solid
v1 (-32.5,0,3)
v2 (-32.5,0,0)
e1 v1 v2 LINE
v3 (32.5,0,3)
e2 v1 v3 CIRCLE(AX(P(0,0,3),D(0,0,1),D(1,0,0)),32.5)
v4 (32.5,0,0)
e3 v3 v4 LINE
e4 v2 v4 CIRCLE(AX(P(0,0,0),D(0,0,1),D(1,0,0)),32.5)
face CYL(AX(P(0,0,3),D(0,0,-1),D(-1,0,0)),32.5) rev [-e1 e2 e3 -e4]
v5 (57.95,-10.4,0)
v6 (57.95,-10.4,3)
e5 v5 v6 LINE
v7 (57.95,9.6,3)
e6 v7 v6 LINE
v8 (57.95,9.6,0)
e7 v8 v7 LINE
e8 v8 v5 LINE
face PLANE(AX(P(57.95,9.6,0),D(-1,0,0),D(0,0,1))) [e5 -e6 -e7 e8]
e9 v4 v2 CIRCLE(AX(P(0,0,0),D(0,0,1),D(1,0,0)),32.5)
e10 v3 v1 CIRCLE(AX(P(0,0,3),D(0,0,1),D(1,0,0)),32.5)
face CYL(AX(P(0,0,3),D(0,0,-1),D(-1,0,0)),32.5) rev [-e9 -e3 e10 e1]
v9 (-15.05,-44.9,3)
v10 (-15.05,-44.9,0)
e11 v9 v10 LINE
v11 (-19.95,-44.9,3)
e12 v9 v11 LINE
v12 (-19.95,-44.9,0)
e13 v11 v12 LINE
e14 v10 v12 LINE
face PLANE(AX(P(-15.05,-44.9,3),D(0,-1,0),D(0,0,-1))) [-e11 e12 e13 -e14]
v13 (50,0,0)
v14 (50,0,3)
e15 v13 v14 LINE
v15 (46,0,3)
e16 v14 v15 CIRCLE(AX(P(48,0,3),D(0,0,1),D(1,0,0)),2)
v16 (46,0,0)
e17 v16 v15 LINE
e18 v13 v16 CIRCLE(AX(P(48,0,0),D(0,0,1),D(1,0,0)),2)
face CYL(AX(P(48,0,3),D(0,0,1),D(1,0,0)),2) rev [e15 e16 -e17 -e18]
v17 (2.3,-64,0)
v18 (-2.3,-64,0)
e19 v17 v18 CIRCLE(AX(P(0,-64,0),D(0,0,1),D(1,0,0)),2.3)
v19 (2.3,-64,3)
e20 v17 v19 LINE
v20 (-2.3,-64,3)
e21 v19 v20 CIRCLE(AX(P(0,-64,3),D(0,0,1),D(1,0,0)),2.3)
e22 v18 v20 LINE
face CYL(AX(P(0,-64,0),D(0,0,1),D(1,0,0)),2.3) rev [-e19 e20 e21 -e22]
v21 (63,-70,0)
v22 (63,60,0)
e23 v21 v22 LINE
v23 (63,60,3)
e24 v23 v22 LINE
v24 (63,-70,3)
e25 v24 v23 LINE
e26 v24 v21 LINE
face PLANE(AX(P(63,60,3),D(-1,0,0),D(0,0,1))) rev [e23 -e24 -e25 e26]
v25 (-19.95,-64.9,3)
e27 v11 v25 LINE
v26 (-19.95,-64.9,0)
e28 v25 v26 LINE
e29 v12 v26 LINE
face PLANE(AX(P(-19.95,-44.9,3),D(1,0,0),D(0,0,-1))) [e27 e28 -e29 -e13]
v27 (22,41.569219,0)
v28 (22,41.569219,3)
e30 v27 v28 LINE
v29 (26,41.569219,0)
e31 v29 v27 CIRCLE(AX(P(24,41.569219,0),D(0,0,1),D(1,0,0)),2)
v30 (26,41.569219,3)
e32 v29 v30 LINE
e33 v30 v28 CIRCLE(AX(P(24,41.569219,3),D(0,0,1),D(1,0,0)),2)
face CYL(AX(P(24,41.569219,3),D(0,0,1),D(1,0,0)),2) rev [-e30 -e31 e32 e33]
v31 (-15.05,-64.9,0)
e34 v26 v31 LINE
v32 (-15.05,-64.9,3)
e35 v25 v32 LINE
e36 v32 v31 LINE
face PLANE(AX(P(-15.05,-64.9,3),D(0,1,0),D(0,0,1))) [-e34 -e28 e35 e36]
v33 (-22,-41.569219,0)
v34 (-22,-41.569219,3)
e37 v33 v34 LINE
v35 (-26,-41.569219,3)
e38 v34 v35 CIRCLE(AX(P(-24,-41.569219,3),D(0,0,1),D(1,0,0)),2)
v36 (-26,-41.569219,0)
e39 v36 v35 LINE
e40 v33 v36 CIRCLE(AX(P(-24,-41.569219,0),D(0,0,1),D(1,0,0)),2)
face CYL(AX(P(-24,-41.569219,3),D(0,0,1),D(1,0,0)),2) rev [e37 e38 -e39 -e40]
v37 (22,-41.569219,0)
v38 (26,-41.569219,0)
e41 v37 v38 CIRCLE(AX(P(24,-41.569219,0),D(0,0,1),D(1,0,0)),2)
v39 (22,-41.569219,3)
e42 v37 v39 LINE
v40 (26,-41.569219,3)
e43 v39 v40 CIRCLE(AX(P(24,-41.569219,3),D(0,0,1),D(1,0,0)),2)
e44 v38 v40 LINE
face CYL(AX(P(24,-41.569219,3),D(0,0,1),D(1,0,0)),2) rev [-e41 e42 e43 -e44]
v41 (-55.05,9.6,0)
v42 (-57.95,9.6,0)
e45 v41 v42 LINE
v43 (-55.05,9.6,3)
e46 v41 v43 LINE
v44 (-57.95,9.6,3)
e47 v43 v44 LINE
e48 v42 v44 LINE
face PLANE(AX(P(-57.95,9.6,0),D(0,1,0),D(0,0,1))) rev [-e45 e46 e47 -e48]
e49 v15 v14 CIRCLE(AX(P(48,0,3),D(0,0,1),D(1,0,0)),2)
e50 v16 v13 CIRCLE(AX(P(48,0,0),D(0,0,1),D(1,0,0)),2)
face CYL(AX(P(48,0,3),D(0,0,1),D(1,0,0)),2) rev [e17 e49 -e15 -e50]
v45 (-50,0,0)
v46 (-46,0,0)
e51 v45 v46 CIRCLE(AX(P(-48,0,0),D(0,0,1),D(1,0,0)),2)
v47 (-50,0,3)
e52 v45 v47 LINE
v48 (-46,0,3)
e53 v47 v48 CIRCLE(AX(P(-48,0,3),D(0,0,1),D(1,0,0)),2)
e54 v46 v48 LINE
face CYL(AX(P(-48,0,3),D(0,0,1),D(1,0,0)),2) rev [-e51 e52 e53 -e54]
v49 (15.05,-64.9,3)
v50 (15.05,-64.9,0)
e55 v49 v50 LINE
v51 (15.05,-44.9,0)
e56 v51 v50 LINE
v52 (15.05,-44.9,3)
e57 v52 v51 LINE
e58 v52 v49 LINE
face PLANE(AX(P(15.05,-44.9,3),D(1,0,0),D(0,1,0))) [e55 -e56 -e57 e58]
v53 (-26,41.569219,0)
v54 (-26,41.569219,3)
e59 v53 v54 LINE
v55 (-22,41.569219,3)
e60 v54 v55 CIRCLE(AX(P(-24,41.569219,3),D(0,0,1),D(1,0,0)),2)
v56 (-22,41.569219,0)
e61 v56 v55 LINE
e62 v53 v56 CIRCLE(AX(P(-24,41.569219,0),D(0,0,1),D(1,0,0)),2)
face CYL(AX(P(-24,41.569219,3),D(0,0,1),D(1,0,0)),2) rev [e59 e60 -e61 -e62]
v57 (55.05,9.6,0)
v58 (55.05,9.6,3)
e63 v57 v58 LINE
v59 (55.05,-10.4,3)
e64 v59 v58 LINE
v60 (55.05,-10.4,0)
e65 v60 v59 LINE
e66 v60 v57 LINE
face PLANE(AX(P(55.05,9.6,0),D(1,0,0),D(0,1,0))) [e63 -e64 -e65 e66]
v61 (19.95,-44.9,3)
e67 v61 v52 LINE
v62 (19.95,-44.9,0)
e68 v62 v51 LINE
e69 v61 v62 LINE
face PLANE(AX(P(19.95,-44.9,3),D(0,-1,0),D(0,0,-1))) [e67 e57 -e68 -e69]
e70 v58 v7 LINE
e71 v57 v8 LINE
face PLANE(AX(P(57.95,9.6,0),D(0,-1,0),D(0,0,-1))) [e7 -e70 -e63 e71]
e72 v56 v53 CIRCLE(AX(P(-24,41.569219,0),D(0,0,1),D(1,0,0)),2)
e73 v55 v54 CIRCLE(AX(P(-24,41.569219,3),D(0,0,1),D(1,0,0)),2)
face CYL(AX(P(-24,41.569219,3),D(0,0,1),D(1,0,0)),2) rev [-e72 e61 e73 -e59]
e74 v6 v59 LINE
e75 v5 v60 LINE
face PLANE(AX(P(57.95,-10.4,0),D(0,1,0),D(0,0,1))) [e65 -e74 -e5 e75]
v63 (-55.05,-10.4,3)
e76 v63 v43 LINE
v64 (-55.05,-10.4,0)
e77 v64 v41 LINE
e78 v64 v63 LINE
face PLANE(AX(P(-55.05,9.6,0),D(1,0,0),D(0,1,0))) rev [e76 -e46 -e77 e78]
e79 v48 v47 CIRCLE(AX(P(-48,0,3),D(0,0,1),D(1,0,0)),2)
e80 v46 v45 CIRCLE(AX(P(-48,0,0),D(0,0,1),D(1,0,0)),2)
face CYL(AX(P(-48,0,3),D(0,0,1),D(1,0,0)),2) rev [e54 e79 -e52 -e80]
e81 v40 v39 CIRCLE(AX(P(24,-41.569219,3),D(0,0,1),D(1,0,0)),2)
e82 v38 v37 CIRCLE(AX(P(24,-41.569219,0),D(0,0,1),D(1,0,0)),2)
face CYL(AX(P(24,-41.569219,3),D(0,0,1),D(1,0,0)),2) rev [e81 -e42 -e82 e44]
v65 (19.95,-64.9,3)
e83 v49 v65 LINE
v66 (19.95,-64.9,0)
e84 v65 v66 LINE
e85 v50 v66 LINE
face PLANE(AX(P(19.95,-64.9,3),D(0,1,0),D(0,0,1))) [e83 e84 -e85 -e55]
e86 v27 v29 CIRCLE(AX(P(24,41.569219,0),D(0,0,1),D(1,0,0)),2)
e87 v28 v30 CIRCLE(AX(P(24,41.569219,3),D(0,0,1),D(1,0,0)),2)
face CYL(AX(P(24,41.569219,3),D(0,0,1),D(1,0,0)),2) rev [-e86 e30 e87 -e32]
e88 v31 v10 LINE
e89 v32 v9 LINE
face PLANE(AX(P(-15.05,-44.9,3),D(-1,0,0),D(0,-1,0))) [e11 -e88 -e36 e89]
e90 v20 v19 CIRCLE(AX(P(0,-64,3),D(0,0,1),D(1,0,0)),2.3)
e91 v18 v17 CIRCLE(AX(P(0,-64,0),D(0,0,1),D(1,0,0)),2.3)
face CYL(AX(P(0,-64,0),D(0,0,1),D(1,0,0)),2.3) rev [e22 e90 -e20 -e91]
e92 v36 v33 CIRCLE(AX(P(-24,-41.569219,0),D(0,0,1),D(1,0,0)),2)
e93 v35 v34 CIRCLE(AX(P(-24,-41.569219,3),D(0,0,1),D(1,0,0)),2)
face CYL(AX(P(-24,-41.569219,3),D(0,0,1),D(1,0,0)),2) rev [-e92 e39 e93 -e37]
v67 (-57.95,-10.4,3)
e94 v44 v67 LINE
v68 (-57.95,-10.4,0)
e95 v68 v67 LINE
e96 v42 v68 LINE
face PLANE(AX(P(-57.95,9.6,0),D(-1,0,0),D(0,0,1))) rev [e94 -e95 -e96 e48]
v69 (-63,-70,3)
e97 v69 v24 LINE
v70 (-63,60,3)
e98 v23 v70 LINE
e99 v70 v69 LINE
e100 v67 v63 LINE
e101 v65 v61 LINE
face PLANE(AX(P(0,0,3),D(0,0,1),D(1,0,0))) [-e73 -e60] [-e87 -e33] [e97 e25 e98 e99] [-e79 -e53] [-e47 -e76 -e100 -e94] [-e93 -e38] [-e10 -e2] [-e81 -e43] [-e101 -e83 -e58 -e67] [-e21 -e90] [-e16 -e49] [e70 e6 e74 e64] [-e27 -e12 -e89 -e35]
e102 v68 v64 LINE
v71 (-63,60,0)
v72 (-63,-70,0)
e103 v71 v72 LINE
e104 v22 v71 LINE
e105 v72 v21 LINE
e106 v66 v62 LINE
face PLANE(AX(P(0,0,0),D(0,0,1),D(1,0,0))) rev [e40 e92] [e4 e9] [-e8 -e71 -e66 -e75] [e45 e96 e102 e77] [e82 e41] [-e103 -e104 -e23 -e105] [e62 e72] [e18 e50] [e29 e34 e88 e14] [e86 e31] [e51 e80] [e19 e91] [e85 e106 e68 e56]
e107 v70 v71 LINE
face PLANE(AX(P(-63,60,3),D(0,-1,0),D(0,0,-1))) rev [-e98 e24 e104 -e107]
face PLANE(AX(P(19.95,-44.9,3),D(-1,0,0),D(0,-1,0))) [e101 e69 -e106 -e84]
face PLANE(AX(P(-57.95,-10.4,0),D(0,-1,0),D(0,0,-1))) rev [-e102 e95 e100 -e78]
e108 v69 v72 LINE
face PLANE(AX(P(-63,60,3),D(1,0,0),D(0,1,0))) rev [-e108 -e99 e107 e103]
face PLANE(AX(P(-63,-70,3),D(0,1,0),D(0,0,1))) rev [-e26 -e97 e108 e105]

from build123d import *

# Parameters (mm, degrees)
SKETCH1_W                    = 126
SKETCH1_H                    = 130
SKETCH1_R                    = 32.5
SKETCH1_W_2                  = 4.9
SKETCH1_H_2                  = 20
BOSS_EXTRUDE1_DEPTH          = 3
SKETCH2_W                    = 2.9
SKETCH2_H                    = 20
CUT_EXTRUDE1_DEPTH           = 3
F_4_0_4_DIAMETER_HOLE1_D     = 4
F_4_0_4_DIAMETER_HOLE1_DEPTH = 10
F_4_0_4_DIAMETER_HOLE1_TIP   = 1.201721238
SKETCH6_R                    = 2.3
CUT_EXTRUDE2_DEPTH           = 3


with BuildPart() as part:
    # Sketch1 → Boss-Extrude1 (new body)
    with BuildSketch(Plane.XY):
        with Locations((0, -5)):
            Rectangle(SKETCH1_W, SKETCH1_H)
        Circle(SKETCH1_R, mode=Mode.SUBTRACT)
        with Locations((-17.5, -54.9)):
            Rectangle(SKETCH1_W_2, SKETCH1_H_2, mode=Mode.SUBTRACT)
        with Locations((17.5, -54.9)):
            Rectangle(SKETCH1_W_2, SKETCH1_H_2, mode=Mode.SUBTRACT)
    extrude(amount=BOSS_EXTRUDE1_DEPTH)

    # Sketch2 → Cut-Extrude1 (cut)
    with BuildSketch(Plane.XY.offset(3)):
        with Locations((-56.5, -0.4)):
            Rectangle(SKETCH2_W, SKETCH2_H)
    cut_extrude1 = extrude(amount=-CUT_EXTRUDE1_DEPTH, mode=Mode.SUBTRACT)

    # Mirror1: Cut-Extrude1 across plane
    add(cut_extrude1.mirror(Plane(origin=(0, 0, 0), x_dir=(0, 0, 1), z_dir=(1, 0, 0))), mode=Mode.SUBTRACT)

    # Ø4.0 (4) Diameter Hole1
    with Locations(Plane.XY.offset(3)):
        with Locations((-24, 41.569219382), (48, 0), (24, 41.569219382), (24, -41.569219382), (-24, -41.569219382), (-48, 0)):
            Hole(F_4_0_4_DIAMETER_HOLE1_D / 2, depth=F_4_0_4_DIAMETER_HOLE1_DEPTH)
            with Locations((0, 0, -(F_4_0_4_DIAMETER_HOLE1_DEPTH + F_4_0_4_DIAMETER_HOLE1_TIP / 2))):  # 118° drill point
                Cone(0, F_4_0_4_DIAMETER_HOLE1_D / 2, F_4_0_4_DIAMETER_HOLE1_TIP, mode=Mode.SUBTRACT)

    # Sketch6 → Cut-Extrude2 (cut)
    with BuildSketch(Plane.XY.offset(3)):
        with Locations((0, -64)):
            Circle(SKETCH6_R)
    extrude(amount=-CUT_EXTRUDE2_DEPTH, mode=Mode.SUBTRACT)


solid = part.part
